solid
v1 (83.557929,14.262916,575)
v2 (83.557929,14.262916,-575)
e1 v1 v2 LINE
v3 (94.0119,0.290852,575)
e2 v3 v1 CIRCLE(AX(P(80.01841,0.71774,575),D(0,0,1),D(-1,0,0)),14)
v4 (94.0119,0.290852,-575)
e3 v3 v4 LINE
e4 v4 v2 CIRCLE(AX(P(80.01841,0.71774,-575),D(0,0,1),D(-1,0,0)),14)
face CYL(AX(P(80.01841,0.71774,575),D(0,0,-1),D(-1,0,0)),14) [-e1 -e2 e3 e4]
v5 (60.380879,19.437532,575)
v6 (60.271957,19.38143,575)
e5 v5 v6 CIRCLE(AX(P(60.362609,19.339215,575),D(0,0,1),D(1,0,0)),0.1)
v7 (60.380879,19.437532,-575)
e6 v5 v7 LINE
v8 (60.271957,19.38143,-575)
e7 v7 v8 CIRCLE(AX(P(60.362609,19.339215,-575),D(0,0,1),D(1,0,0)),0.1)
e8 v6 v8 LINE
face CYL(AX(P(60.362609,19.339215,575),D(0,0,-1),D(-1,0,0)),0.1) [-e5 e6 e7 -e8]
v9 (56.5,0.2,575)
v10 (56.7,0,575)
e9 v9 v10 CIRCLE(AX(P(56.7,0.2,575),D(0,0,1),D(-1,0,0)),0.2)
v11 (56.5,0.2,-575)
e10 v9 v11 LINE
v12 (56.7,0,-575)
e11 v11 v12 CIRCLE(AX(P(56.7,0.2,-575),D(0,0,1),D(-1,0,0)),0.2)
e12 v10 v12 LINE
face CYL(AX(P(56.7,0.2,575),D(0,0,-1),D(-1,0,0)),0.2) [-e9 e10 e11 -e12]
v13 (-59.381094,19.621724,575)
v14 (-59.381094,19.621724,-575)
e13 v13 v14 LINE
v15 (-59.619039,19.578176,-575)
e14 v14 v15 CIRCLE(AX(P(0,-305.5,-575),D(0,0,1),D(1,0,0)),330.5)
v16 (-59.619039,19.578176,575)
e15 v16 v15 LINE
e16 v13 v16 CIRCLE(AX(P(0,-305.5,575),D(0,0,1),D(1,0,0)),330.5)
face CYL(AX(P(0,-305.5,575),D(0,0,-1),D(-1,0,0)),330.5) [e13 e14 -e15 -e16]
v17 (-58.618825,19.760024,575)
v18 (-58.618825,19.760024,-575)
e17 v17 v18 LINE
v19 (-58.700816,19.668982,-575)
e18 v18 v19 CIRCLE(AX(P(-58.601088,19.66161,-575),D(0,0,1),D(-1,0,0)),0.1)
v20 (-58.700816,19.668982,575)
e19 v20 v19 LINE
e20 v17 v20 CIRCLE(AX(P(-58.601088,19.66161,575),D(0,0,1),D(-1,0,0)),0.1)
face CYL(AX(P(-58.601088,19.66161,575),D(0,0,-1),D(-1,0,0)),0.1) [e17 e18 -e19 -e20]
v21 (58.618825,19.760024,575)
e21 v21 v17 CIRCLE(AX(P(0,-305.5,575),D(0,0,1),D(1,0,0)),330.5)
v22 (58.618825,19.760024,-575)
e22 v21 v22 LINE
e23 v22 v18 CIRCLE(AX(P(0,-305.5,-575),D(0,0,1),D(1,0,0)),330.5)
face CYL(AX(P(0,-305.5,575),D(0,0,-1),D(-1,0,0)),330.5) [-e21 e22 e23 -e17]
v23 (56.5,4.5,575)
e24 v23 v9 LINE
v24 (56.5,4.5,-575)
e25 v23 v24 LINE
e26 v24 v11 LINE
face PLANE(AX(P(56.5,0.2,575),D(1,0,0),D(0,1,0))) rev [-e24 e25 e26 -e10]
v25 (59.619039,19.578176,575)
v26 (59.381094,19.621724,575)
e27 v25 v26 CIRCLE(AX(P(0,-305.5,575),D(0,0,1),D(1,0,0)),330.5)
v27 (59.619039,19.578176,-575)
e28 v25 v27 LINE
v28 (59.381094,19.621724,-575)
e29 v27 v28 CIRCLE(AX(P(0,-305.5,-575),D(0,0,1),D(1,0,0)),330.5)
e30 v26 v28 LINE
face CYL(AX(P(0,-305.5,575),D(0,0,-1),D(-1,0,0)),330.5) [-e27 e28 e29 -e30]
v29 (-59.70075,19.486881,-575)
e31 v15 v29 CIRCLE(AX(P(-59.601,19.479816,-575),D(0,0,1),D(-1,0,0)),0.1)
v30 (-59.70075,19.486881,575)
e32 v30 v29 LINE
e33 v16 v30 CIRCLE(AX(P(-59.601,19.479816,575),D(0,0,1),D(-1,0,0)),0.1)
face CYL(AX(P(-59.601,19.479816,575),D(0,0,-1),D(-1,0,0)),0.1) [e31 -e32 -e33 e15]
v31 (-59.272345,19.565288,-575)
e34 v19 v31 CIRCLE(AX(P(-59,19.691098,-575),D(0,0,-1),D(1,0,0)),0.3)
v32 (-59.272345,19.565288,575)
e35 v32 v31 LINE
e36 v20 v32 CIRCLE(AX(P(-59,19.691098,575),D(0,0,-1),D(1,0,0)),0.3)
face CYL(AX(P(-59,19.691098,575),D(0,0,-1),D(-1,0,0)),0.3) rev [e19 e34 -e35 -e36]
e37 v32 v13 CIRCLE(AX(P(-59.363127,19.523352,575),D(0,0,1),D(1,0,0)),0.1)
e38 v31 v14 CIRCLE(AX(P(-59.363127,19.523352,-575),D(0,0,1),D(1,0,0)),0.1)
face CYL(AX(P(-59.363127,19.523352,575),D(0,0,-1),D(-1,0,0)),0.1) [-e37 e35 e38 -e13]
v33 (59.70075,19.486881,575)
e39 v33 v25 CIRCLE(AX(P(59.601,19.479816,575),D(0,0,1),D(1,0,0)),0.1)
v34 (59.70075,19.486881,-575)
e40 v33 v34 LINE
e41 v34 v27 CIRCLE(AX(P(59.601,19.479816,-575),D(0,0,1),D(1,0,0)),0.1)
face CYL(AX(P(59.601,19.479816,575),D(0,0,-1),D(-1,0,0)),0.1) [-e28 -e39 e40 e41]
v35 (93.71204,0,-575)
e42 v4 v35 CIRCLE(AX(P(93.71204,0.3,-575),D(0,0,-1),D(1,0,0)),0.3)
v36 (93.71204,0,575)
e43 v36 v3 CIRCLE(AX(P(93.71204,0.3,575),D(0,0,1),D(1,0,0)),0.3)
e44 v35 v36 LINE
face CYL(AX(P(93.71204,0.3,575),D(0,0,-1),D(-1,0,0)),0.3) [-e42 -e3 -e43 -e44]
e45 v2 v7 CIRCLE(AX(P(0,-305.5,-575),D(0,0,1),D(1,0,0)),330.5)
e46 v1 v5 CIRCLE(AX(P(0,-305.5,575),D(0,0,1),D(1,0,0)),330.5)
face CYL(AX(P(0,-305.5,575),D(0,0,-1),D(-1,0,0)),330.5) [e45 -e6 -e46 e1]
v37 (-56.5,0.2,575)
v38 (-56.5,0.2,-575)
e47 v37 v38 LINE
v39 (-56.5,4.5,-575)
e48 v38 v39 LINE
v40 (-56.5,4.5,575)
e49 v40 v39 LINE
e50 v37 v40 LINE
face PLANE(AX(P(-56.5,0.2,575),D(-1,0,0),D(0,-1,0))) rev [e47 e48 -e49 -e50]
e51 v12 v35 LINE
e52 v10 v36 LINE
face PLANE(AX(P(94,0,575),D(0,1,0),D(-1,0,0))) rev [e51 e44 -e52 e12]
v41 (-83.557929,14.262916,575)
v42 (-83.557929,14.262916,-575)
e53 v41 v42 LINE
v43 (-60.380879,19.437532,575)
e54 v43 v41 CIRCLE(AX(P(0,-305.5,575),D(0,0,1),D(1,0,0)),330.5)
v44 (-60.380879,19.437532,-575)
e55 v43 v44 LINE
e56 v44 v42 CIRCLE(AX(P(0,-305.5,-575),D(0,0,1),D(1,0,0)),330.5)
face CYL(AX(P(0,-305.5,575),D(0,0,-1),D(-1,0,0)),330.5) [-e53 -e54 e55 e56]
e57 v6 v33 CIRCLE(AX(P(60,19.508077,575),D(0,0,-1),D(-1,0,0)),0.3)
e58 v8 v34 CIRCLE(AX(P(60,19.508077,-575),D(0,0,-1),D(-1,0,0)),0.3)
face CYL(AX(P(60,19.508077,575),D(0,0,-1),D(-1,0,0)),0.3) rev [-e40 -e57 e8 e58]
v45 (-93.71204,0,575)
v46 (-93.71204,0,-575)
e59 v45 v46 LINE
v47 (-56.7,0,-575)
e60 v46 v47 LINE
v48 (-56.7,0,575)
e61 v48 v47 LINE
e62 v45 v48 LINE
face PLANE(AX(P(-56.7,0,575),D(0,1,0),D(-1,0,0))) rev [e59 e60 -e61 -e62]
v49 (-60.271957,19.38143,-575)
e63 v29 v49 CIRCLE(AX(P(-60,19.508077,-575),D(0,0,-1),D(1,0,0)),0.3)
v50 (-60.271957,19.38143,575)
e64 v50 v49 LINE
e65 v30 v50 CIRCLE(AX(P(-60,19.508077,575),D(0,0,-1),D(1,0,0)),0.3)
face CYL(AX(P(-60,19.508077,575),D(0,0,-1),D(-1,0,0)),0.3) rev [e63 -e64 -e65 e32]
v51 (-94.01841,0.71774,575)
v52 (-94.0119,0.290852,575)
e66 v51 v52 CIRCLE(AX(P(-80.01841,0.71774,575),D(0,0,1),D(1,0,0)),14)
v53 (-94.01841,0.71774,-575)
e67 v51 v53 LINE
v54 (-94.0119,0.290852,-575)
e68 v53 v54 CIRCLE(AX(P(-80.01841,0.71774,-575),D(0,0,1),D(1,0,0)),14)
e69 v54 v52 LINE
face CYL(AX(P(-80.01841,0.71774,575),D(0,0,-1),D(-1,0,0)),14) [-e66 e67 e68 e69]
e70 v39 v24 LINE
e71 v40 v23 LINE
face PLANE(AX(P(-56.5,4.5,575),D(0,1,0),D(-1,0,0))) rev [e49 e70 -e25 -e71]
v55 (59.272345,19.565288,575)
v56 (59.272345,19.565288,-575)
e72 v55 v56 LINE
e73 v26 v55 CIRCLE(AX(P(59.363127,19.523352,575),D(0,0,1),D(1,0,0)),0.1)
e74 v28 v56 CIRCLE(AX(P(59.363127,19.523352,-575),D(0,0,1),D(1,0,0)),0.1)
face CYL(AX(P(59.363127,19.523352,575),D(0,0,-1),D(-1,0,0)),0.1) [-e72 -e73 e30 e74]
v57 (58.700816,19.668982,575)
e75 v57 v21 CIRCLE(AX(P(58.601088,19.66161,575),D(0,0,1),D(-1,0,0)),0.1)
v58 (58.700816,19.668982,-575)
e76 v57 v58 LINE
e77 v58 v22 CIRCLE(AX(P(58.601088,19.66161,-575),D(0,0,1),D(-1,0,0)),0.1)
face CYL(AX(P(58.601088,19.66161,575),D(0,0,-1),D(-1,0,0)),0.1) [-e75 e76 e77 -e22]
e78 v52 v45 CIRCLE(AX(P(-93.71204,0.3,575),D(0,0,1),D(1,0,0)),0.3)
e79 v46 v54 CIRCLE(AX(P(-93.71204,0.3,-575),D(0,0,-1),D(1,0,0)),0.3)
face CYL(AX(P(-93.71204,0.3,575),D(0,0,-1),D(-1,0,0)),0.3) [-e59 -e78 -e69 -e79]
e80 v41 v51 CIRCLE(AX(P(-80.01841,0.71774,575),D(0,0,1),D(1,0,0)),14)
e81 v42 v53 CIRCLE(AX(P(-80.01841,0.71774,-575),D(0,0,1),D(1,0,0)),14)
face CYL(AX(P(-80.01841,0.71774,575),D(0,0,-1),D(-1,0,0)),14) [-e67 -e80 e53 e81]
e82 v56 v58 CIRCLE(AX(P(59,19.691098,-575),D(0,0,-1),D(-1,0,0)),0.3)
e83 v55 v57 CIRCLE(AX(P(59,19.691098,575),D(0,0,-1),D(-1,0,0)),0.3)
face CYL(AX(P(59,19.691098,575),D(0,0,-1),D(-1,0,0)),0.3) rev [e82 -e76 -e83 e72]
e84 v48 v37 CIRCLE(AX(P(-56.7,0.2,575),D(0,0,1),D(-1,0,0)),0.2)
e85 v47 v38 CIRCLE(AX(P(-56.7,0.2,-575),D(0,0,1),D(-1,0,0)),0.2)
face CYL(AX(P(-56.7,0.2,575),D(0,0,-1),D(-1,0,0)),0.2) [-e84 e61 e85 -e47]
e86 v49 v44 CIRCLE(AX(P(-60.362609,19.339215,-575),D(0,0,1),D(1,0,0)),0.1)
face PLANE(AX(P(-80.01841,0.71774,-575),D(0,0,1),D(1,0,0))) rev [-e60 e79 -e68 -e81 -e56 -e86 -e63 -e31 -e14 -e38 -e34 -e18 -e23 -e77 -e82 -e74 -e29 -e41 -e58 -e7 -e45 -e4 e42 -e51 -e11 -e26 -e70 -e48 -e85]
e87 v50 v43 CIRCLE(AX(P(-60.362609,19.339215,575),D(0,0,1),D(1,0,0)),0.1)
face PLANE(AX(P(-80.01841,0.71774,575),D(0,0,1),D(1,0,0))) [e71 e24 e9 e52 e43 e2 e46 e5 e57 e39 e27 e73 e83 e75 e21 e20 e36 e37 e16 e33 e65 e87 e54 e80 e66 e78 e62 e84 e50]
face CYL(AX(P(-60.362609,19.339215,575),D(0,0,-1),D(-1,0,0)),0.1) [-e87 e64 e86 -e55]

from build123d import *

# Parameters (mm, degrees)
EXTRUDE_1_DEPTH = 575
FILLET_1_R      = 0.3


with BuildPart() as part:
    # 草图1 → 凸台-拉伸1 (new, symmetric)
    with BuildSketch(Plane.XY):
        with BuildLine():
            Line((94, 0), (56.7, 0))
            ThreePointArc((56.7, 0), (56.558578644, 0.058578644), (56.5, 0.2))
            Line((56.5, 0.2), (56.5, 4.5))
            Line((56.5, 4.5), (-56.5, 4.5))
            Line((-56.5, 4.5), (-56.5, 0.2))
            ThreePointArc((-56.5, 0.2), (-56.558578644, 0.058578644), (-56.7, 0))
            Line((-56.7, 0), (-94, 0))
            ThreePointArc((-94, 0), (-91.314648859, 8.987866196), (-83.557929261, 14.262916014))
            ThreePointArc((-83.557929261, 14.262916014), (-72.015896085, 17.05846092), (-60.38087895, 19.437531623))
            ThreePointArc((-60.38087895, 19.437531623), (-60.316820101, 19.428115404), (-60.271957046, 19.381430208))
            ThreePointArc((-60.271957046, 19.381430208), (-59.945537065, 19.213061927), (-59.70074969, 19.486881253))
            ThreePointArc((-59.70074969, 19.486881253), (-59.675512901, 19.546507637), (-59.619038631, 19.578175571))
            ThreePointArc((-59.619038631, 19.578175571), (-59.500070371, 19.599971741), (-59.381094143, 19.621724372))
            ThreePointArc((-59.381094143, 19.621724372), (-59.317064562, 19.612111154), (-59.272345321, 19.565288181))
            ThreePointArc((-59.272345321, 19.565288181), (-58.946444781, 19.395916638), (-58.700816303, 19.668981709))
            ThreePointArc((-58.700816303, 19.668981709), (-58.675396224, 19.728530183), (-58.618824811, 19.760024254))
            ThreePointArc((-58.618824811, 19.760024254), (0, 25), (58.618824811, 19.760024254))
            ThreePointArc((58.618824811, 19.760024254), (58.675396224, 19.728530183), (58.700816303, 19.668981709))
            ThreePointArc((58.700816303, 19.668981709), (58.946444781, 19.395916638), (59.272345321, 19.565288181))
            ThreePointArc((59.272345321, 19.565288181), (59.317064562, 19.612111154), (59.381094143, 19.621724372))
            ThreePointArc((59.381094143, 19.621724372), (59.500070371, 19.599971741), (59.619038631, 19.578175571))
            ThreePointArc((59.619038631, 19.578175571), (59.675512901, 19.546507637), (59.70074969, 19.486881253))
            ThreePointArc((59.70074969, 19.486881253), (59.945537065, 19.213061927), (60.271957046, 19.381430208))
            ThreePointArc((60.271957046, 19.381430208), (60.316820101, 19.428115404), (60.38087895, 19.437531623))
            ThreePointArc((60.38087895, 19.437531623), (72.015896085, 17.05846092), (83.557929261, 14.262916014))
            ThreePointArc((83.557929261, 14.262916014), (91.314648859, 8.987866196), (94, 0))
        make_face()
    extrude(amount=EXTRUDE_1_DEPTH, both=True)

    # 圆角1
    fillet_1_edges = [part.edges().sort_by_distance(p)[0] for p in [
        (94, 0, 0),
        (-94, 0, 0),
    ]]
    fillet(fillet_1_edges, radius=FILLET_1_R)


solid = part.part
